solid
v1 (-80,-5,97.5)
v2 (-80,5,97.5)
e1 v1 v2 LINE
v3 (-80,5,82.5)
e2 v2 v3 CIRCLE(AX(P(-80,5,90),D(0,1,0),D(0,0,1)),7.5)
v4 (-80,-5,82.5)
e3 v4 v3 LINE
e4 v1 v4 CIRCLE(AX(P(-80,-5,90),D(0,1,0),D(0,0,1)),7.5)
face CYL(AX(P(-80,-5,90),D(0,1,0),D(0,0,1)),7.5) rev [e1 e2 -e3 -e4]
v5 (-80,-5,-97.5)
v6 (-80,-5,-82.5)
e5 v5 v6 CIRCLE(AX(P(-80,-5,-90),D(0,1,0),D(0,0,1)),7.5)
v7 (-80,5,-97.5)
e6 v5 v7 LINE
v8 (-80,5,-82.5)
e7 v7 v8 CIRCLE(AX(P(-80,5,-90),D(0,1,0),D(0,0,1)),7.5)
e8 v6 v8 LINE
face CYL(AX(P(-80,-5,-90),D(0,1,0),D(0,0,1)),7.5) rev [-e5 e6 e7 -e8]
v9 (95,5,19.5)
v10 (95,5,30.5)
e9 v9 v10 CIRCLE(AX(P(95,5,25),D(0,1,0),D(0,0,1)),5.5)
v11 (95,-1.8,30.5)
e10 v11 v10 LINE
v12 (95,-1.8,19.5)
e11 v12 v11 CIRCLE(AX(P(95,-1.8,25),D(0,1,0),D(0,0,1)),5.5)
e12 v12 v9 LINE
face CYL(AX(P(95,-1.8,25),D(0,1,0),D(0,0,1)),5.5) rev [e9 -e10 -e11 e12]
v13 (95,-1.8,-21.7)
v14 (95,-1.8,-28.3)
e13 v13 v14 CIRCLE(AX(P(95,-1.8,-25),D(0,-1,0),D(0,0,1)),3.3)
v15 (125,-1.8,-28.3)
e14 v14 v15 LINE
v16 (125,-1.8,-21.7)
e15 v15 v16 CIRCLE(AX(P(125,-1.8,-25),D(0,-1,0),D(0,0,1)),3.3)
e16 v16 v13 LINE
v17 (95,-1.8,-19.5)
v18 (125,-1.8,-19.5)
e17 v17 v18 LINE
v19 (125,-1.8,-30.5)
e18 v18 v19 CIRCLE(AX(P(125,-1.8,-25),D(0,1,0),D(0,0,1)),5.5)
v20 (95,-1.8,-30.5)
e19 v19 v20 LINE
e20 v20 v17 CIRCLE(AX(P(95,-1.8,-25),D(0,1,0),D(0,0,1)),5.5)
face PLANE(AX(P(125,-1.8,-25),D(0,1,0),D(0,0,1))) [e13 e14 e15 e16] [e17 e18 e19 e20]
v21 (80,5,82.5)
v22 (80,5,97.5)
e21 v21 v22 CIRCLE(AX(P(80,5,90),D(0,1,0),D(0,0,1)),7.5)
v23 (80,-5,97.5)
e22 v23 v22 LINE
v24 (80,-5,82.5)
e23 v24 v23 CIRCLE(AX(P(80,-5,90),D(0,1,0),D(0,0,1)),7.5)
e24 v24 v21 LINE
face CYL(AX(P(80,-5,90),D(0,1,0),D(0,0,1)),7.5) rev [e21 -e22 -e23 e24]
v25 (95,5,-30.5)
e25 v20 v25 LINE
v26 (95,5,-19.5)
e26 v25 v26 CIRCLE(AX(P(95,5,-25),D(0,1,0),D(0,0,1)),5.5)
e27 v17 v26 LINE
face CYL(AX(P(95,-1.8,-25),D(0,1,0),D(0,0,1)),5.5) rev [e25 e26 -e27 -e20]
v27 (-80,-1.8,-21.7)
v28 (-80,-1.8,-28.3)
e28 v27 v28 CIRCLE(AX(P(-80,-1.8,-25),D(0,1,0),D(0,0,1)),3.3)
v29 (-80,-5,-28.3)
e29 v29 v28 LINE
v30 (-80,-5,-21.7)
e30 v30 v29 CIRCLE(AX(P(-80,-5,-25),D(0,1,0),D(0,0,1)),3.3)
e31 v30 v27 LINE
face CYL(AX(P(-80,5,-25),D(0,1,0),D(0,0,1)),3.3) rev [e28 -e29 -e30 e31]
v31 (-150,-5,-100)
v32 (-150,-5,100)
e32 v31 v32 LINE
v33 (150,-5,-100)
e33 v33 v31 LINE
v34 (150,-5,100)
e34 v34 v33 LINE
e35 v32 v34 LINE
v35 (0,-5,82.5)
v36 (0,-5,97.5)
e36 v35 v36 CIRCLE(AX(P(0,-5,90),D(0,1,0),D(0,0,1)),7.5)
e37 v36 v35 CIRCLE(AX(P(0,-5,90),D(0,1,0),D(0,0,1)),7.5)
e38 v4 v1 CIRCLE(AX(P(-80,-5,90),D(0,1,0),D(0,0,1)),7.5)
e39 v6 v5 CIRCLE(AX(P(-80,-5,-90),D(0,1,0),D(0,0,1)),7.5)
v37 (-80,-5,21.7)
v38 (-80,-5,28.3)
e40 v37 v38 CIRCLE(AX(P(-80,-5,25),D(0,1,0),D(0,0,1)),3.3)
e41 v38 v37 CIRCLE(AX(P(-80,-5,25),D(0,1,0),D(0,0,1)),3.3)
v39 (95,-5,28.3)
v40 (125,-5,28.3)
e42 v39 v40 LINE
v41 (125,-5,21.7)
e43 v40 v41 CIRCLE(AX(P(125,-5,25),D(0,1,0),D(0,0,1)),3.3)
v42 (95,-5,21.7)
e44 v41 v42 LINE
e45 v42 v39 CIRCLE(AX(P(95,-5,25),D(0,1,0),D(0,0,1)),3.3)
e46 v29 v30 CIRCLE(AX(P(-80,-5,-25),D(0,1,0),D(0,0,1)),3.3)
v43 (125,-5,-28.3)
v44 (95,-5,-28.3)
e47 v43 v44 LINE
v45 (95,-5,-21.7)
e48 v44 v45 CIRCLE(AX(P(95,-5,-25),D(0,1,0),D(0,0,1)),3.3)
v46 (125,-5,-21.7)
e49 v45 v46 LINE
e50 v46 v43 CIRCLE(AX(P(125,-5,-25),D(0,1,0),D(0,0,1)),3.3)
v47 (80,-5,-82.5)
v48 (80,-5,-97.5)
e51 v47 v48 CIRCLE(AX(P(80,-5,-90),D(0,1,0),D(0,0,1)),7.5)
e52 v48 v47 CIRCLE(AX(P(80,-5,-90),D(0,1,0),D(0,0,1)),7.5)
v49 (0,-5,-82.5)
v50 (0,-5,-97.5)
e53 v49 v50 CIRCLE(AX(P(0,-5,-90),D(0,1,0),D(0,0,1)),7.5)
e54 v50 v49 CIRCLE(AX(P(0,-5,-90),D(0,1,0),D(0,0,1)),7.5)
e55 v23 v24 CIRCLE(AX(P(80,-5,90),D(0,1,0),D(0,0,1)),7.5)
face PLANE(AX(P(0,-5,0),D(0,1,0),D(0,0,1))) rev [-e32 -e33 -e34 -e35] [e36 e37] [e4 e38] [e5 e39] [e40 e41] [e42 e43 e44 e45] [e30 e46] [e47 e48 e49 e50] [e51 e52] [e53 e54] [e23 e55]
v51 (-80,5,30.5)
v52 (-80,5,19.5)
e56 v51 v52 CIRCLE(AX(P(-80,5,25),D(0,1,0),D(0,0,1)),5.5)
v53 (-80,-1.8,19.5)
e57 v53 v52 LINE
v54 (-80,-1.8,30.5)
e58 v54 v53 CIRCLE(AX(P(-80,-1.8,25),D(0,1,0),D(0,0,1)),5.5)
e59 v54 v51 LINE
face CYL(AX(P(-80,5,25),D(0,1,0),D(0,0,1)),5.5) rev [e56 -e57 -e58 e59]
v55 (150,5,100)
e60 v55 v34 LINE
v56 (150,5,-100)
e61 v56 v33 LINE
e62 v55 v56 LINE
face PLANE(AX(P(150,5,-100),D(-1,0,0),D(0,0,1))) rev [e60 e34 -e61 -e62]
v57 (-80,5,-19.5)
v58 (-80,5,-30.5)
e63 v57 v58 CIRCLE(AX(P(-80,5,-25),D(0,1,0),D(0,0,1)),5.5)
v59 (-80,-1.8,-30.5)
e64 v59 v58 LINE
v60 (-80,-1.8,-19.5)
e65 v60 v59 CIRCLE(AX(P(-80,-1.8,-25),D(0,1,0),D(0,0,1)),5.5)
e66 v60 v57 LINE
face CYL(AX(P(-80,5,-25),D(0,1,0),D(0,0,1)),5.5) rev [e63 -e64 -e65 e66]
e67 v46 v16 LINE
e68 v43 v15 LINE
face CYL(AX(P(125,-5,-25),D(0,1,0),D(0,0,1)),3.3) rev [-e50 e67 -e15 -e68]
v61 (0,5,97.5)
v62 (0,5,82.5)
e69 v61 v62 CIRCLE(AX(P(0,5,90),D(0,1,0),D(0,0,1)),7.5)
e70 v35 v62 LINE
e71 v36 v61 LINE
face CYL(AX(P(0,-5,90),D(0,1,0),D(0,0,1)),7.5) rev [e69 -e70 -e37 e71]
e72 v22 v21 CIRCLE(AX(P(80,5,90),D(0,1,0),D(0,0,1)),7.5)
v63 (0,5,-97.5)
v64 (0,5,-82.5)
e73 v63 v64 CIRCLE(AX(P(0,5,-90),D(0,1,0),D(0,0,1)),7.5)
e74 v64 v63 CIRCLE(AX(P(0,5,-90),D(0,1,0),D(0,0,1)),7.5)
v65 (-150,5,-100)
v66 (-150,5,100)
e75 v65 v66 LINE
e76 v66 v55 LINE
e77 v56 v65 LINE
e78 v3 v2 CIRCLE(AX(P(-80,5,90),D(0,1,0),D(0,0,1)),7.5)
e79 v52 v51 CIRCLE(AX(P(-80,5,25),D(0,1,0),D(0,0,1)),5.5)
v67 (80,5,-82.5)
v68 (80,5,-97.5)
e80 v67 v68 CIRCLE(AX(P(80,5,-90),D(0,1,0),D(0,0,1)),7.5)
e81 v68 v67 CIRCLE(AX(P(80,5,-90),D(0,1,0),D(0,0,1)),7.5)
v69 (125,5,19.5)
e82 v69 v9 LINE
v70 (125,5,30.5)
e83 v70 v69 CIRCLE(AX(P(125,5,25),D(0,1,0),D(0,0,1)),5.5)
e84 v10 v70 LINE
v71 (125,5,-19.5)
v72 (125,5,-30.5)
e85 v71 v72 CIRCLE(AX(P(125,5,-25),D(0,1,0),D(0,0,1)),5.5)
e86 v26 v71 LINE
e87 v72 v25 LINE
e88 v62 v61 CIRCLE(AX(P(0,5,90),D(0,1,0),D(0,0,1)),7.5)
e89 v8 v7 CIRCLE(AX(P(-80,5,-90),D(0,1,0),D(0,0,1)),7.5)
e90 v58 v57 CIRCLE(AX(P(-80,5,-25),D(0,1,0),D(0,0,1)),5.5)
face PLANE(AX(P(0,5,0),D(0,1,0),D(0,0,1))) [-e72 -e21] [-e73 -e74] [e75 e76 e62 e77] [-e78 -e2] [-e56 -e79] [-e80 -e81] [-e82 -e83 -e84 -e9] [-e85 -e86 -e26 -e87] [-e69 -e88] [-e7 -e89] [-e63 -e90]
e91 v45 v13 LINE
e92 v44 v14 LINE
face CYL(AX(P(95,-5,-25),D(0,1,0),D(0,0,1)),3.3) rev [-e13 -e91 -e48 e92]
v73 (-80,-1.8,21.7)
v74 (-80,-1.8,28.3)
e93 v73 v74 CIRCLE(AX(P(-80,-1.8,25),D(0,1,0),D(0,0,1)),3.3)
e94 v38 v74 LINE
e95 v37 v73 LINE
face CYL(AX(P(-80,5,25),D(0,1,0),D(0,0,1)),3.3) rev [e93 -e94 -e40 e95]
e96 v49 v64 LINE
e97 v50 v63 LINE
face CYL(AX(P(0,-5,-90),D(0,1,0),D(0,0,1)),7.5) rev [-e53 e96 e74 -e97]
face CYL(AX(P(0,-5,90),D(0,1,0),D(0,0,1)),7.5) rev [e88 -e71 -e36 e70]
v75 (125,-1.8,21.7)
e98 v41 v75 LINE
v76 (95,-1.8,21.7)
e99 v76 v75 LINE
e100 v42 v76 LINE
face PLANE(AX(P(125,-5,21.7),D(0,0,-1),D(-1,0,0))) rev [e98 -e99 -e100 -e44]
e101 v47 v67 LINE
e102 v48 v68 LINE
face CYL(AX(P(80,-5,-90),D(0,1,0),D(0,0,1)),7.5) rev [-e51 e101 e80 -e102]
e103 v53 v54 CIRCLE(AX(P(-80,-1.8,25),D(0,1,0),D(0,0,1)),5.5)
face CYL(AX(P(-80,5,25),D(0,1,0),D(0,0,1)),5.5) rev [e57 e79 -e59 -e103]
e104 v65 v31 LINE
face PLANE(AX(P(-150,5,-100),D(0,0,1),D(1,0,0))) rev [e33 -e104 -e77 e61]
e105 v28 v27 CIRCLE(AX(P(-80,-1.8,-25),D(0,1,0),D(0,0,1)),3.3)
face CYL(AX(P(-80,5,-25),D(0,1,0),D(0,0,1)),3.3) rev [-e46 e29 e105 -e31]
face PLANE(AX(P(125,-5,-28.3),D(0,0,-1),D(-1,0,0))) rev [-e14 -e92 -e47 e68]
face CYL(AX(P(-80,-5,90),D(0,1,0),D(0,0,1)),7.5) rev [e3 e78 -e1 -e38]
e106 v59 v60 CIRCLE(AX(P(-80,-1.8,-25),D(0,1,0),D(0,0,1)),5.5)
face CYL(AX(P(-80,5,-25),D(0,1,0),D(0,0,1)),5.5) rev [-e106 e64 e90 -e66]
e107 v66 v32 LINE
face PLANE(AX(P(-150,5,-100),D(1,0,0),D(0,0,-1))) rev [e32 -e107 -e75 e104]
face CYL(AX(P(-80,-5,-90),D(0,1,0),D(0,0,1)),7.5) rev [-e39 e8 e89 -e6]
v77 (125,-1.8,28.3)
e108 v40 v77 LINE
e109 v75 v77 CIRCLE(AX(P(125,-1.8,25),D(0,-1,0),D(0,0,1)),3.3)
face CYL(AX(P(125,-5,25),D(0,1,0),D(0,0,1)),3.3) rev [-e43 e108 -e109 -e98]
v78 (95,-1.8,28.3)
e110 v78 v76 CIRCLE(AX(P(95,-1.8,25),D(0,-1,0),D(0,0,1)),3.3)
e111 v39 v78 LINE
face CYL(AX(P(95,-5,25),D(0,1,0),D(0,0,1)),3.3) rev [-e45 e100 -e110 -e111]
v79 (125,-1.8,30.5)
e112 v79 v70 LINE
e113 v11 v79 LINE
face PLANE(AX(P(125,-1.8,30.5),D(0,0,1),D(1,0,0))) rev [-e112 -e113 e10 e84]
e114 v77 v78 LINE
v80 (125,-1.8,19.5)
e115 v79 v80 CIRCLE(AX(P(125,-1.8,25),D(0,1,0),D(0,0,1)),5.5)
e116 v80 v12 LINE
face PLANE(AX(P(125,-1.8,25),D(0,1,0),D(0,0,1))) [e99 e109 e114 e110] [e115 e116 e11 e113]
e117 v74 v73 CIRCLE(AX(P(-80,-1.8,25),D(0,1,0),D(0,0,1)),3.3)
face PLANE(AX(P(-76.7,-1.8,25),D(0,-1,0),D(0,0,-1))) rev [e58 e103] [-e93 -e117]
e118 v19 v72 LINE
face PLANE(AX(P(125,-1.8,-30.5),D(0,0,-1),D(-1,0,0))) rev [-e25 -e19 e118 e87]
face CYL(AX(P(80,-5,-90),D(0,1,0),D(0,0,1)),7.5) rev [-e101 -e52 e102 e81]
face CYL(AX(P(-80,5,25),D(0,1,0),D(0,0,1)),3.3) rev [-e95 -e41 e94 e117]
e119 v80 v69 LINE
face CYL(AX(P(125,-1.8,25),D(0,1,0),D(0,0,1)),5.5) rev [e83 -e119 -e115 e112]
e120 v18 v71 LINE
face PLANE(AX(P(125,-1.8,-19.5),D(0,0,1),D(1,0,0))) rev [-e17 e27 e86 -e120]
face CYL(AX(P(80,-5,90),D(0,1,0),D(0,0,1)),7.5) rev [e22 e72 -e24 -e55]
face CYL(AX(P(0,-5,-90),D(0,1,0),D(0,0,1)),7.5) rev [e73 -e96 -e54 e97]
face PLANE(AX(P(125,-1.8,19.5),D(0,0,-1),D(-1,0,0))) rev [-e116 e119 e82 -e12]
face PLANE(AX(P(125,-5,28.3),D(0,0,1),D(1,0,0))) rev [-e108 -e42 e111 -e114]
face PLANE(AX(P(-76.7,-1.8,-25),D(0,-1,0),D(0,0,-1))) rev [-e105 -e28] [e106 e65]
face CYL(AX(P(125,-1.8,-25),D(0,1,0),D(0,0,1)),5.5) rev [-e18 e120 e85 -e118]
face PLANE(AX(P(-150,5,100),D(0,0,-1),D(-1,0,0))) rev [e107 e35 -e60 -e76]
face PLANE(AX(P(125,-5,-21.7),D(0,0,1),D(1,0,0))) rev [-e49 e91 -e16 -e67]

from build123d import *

# Parameters (mm, degrees)
SKETCH1_W                                           = 300
SKETCH1_H                                           = 200
BOSS_EXTRUDE1_DEPTH                                 = 5
SKETCH2_R                                           = 7.5
CUT_EXTRUDE1_DEPTH                                  = 10
LPATTERN1_COUNT                                     = 2
LPATTERN1_PITCH                                     = 180
LPATTERN1_COUNT_DIR2                                = 3
LPATTERN1_PITCH_DIR2                                = 80
HOLE_SIZE_BASED_ON_SOCKET_HEAD_CAP_SCRE_D           = 6.6
HOLE_SIZE_BASED_ON_SOCKET_HEAD_CAP_SCRE_CBORE_D     = 11
HOLE_SIZE_BASED_ON_SOCKET_HEAD_CAP_SCRE_CBORE_DEPTH = 6.8
CUT_EXTRUDE2_DEPTH                                  = 10
CUT_EXTRUDE3_DEPTH                                  = 6.8


with BuildPart() as part:
    # Sketch1 → Boss-Extrude1 (new, symmetric)
    with BuildSketch(Plane(origin=(0, 0, 0), x_dir=(1, 0, 0), z_dir=(0, 1, 0))):
        Rectangle(SKETCH1_W, SKETCH1_H)
    extrude(amount=BOSS_EXTRUDE1_DEPTH, both=True)

    # Sketch2 → Cut-Extrude1 (cut)
    with BuildSketch(Plane(origin=(0, 5, 0), x_dir=(1, 0, 0), z_dir=(0, 1, 0))):
        with Locations(Location((80, 90, 0), (0, 0, 270))):
            Circle(SKETCH2_R)
    cut_extrude1 = extrude(amount=-CUT_EXTRUDE1_DEPTH, mode=Mode.SUBTRACT)

    # LPattern1: Cut-Extrude1 2 × 3
    with Locations(*[(-j * LPATTERN1_PITCH_DIR2, 0, i * LPATTERN1_PITCH) for i in range(LPATTERN1_COUNT) for j in range(LPATTERN1_COUNT_DIR2) if (i, j) != (0, 0)]):
        add(cut_extrude1, mode=Mode.SUBTRACT)

    # Hole Size (based on socket head cap screw type)1 (through all)
    with Locations(Plane(origin=(0, 5, 0), x_dir=(1, 0, 0), z_dir=(0, 1, 0))):
        with Locations((-80, 25), (-80, -25)):
            CounterBoreHole(HOLE_SIZE_BASED_ON_SOCKET_HEAD_CAP_SCRE_D / 2, HOLE_SIZE_BASED_ON_SOCKET_HEAD_CAP_SCRE_CBORE_D / 2, HOLE_SIZE_BASED_ON_SOCKET_HEAD_CAP_SCRE_CBORE_DEPTH)

    # Sketch6 → Cut-Extrude2 (cut)
    with BuildSketch(Plane(origin=(0, 5, 0), x_dir=(1, 0, 0), z_dir=(0, 1, 0))):
        with BuildLine():
            Line((125, 21.7), (95, 21.7))
            ThreePointArc((95, 21.7), (91.7, 25), (95, 28.3))
            Line((95, 28.3), (125, 28.3))
            ThreePointArc((125, 28.3), (128.3, 25), (125, 21.7))
        make_face()
        with BuildLine():
            Line((125, -28.3), (95, -28.3))
            ThreePointArc((95, -28.3), (91.7, -25), (95, -21.7))
            Line((95, -21.7), (125, -21.7))
            ThreePointArc((125, -21.7), (128.3, -25), (125, -28.3))
        make_face()
    extrude(amount=-CUT_EXTRUDE2_DEPTH, mode=Mode.SUBTRACT)

    # Sketch7 → Cut-Extrude3 (cut)
    with BuildSketch(Plane(origin=(0, 5, 0), x_dir=(1, 0, 0), z_dir=(0, 1, 0))):
        with BuildLine():
            Line((125, 19.5), (95, 19.5))
            ThreePointArc((95, 19.5), (89.5, 25), (95, 30.5))
            Line((95, 30.5), (125, 30.5))
            ThreePointArc((125, 30.5), (130.5, 25), (125, 19.5))
        make_face()
        with BuildLine():
            Line((125, -30.5), (95, -30.5))
            ThreePointArc((95, -30.5), (89.5, -25), (95, -19.5))
            Line((95, -19.5), (125, -19.5))
            ThreePointArc((125, -19.5), (130.5, -25), (125, -30.5))
        make_face()
    extrude(amount=-CUT_EXTRUDE3_DEPTH, mode=Mode.SUBTRACT)


solid = part.part
